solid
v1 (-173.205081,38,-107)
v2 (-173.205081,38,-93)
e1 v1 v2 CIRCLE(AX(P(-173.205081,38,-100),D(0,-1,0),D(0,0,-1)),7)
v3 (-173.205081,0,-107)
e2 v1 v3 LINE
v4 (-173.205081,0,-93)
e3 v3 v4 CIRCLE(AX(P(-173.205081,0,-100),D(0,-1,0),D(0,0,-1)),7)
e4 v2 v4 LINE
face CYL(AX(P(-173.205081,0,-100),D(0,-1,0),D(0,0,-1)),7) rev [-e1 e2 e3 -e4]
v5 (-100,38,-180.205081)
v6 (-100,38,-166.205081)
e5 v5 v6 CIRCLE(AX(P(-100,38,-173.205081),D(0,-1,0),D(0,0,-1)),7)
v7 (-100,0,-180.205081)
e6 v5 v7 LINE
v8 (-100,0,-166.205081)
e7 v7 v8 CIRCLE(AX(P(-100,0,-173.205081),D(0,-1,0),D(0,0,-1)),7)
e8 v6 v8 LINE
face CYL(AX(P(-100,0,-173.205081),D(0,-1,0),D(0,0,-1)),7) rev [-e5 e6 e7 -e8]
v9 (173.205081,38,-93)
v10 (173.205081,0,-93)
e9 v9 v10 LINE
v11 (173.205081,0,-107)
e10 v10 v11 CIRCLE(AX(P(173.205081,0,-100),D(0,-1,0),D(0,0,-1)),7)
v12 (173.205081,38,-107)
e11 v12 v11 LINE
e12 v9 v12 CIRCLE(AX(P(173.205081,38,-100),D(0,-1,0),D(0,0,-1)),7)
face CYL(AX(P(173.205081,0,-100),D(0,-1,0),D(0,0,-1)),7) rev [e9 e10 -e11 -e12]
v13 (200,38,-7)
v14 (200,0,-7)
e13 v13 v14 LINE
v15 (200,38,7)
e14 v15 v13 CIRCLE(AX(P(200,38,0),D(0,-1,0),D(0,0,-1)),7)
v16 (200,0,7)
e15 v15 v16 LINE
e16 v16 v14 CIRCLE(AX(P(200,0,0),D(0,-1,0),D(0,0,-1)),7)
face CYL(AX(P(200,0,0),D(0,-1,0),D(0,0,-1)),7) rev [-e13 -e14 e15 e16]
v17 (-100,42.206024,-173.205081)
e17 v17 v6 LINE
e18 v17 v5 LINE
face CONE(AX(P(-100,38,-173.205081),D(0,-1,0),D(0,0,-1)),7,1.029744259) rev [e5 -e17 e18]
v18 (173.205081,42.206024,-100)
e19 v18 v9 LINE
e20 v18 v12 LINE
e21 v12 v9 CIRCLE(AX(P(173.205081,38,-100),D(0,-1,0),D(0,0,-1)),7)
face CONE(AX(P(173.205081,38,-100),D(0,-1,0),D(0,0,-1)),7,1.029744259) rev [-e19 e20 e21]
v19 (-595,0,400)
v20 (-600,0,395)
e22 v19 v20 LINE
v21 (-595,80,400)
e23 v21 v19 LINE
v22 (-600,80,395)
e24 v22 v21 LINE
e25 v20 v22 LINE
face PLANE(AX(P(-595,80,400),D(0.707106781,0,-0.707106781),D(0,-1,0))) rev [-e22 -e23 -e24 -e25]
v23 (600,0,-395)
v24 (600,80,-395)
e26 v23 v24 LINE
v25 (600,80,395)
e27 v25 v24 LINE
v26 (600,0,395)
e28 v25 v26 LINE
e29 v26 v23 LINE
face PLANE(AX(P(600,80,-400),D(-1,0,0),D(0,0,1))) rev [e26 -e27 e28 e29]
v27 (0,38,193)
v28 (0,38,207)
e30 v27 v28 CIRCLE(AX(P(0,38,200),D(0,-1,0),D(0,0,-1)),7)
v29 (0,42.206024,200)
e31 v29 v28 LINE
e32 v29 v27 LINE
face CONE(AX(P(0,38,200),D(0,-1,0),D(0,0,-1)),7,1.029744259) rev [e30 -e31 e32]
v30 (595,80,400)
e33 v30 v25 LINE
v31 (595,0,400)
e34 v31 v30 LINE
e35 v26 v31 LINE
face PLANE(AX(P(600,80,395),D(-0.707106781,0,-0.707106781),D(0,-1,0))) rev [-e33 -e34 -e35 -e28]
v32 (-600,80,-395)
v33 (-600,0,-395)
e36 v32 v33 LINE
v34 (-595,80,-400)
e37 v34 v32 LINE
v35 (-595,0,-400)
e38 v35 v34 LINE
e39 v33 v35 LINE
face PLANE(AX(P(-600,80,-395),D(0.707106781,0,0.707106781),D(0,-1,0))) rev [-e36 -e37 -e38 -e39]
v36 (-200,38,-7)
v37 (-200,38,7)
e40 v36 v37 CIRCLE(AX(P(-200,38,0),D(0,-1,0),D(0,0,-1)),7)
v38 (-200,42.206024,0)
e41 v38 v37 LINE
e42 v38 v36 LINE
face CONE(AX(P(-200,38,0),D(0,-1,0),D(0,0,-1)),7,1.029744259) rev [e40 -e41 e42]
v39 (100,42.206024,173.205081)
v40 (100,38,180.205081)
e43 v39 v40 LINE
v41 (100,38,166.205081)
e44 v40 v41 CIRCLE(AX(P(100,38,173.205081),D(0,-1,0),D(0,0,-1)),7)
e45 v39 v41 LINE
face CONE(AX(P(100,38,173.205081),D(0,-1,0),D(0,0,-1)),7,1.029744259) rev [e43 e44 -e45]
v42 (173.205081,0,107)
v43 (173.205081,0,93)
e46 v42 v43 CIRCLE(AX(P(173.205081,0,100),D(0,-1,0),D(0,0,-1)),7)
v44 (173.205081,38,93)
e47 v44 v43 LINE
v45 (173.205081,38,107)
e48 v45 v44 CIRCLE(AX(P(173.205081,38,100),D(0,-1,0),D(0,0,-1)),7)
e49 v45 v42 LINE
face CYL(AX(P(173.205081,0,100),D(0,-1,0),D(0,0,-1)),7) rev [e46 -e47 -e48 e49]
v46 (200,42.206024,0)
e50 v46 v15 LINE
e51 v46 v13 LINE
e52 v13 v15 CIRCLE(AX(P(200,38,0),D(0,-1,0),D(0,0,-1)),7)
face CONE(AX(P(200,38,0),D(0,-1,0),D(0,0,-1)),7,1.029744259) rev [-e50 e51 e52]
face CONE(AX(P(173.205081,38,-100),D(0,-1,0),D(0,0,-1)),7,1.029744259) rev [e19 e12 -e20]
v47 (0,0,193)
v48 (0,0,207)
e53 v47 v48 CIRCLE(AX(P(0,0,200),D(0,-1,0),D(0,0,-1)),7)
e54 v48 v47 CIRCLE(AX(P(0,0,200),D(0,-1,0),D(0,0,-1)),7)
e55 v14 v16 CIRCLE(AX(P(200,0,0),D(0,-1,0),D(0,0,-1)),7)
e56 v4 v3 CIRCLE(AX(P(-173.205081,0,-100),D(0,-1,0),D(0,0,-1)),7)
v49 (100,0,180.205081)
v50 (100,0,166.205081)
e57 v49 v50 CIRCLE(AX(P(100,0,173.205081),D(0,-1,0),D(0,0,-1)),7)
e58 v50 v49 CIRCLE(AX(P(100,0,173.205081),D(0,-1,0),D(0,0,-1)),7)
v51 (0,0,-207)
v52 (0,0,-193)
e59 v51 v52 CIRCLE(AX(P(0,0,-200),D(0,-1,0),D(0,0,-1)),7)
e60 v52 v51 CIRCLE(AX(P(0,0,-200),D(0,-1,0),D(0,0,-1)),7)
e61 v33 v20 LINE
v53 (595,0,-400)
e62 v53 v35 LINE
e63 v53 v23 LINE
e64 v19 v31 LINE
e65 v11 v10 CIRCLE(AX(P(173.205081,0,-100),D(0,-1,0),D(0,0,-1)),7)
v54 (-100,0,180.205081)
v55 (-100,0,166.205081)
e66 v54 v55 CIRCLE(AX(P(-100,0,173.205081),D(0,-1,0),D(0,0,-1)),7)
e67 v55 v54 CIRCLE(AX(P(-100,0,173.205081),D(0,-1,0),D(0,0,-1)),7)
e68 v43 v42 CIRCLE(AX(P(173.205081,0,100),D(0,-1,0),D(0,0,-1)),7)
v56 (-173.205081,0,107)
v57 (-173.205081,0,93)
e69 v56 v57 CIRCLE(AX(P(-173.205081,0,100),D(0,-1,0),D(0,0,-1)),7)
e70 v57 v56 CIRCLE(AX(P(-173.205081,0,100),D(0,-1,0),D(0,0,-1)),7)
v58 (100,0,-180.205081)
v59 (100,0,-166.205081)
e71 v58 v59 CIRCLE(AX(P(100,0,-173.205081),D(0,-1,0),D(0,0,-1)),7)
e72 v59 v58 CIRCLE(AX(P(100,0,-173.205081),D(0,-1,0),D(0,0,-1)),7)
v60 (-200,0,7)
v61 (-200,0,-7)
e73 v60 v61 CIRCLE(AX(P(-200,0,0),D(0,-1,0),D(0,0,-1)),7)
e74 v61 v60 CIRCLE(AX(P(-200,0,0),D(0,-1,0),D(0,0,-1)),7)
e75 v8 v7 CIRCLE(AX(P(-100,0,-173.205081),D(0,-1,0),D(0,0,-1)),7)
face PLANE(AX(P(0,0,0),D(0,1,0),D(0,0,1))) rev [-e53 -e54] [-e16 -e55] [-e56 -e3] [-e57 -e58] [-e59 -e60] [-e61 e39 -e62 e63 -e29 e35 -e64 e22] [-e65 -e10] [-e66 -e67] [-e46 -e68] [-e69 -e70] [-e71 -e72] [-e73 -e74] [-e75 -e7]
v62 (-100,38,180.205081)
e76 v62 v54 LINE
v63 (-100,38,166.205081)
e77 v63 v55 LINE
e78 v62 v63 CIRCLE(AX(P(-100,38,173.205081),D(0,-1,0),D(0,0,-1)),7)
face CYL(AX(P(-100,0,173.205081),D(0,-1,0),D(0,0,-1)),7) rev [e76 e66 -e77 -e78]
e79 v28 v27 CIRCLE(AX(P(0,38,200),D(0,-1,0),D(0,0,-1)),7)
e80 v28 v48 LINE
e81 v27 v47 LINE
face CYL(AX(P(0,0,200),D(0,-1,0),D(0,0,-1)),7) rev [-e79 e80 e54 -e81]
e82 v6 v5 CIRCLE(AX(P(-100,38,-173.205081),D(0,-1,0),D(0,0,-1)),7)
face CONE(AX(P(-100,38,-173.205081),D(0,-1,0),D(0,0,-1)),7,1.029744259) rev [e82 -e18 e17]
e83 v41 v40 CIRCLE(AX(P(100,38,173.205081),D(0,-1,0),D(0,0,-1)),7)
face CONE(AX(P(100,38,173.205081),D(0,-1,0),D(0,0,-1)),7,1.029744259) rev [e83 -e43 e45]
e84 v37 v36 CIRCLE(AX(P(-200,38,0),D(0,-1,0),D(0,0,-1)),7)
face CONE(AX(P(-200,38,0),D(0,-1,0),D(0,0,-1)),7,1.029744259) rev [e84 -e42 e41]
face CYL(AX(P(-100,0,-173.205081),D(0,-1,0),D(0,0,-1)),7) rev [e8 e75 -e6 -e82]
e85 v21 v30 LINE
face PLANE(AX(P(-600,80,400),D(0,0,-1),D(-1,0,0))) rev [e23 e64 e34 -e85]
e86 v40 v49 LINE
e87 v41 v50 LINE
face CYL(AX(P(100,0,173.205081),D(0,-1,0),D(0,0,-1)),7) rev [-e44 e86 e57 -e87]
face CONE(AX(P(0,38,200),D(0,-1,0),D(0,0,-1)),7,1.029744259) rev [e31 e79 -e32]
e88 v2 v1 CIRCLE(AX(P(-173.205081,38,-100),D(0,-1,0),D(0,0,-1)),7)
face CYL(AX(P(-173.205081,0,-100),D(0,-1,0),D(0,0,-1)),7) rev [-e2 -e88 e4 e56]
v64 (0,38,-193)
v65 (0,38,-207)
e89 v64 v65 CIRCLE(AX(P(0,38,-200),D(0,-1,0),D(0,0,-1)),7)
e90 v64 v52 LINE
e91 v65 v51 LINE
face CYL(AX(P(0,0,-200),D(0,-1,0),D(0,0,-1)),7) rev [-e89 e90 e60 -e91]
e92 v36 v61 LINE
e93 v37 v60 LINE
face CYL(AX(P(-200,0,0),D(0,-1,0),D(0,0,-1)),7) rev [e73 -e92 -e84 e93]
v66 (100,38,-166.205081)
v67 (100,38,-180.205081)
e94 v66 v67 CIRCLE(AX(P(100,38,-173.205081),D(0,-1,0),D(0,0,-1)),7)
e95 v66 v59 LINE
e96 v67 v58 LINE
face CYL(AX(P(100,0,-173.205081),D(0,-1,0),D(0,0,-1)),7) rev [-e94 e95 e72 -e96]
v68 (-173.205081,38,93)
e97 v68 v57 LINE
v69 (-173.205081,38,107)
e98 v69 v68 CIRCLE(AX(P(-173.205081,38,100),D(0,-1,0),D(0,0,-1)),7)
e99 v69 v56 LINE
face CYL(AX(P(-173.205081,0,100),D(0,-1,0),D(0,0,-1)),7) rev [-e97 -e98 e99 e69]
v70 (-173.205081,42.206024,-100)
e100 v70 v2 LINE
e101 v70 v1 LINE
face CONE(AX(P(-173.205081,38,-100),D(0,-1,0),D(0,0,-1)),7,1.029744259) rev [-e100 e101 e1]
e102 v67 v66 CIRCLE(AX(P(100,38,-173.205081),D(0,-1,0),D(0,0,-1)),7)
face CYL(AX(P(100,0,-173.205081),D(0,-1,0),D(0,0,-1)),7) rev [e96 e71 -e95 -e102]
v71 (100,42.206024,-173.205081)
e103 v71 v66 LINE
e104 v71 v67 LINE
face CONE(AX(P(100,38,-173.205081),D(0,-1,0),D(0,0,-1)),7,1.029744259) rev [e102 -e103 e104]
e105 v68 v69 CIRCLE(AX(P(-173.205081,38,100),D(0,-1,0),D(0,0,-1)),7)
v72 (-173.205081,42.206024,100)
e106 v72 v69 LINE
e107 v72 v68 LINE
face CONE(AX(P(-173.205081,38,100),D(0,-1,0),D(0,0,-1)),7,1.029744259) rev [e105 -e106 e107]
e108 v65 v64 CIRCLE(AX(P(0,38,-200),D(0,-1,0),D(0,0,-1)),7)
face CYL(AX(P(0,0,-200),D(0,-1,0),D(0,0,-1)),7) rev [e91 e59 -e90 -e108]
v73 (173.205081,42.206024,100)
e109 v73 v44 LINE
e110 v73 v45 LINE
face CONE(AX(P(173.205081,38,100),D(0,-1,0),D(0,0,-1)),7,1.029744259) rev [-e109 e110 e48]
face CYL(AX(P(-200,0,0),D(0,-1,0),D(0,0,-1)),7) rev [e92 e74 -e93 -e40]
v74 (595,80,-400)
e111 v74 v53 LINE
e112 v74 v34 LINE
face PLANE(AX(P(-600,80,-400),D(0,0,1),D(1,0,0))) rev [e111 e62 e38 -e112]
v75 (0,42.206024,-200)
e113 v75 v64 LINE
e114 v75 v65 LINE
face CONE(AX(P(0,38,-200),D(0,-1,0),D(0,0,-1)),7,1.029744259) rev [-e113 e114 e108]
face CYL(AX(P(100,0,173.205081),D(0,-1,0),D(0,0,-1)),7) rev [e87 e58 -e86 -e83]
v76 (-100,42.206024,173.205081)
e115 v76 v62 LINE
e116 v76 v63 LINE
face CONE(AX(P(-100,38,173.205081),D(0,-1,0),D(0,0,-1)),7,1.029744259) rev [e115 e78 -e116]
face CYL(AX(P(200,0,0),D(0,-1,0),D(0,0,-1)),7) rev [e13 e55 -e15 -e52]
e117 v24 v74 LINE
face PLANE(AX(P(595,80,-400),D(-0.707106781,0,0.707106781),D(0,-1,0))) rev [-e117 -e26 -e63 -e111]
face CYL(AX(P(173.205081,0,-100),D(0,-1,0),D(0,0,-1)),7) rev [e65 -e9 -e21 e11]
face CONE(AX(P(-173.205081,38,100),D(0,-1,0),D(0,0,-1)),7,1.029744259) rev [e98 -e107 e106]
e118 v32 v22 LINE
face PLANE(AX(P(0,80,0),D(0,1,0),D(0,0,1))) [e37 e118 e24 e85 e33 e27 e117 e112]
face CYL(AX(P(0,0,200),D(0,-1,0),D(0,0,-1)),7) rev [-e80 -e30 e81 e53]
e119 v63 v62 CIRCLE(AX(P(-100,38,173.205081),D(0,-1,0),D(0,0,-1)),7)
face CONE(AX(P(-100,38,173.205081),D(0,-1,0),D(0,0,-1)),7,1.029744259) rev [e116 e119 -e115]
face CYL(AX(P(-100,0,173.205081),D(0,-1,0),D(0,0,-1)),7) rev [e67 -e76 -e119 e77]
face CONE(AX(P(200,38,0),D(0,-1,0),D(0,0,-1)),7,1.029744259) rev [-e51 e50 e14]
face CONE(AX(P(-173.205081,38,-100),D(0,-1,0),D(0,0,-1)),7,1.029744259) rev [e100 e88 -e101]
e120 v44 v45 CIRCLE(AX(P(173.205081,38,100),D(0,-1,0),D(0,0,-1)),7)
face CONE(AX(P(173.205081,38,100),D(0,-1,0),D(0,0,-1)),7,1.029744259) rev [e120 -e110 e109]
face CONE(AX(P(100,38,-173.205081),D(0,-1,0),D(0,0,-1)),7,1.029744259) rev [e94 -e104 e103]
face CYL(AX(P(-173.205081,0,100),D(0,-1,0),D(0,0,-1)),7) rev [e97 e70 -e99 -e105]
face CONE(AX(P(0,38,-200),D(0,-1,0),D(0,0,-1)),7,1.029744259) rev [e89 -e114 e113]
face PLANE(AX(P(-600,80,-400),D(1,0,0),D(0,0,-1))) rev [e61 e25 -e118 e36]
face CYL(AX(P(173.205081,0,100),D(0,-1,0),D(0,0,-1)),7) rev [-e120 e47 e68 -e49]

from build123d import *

# Parameters (mm, degrees)
SKETCH1_W              = 1200
SKETCH1_H              = 800
BOSS_EXTRUDE1_DEPTH    = 80
CHAMFER1_SIZE          = 5
M16_TAPPED_HOLE1_D     = 14
M16_TAPPED_HOLE1_DEPTH = 38
M16_TAPPED_HOLE1_TIP   = 4.206024333


with BuildPart() as part:
    # Sketch1 → Boss-Extrude1 (new body)
    with BuildSketch(Plane(origin=(0, 0, 0), x_dir=(1, 0, 0), z_dir=(0, 1, 0))):
        Rectangle(SKETCH1_W, SKETCH1_H)
    extrude(amount=BOSS_EXTRUDE1_DEPTH)

    # Chamfer1
    chamfer1_edges = [part.edges().sort_by_distance(p)[0] for p in [
        (600, 40, 400),
        (-600, 40, 400),
        (-600, 40, -400),
        (600, 40, -400),
    ]]
    chamfer(chamfer1_edges, length=CHAMFER1_SIZE)

    # M16 Tapped Hole1
    with Locations(Plane(origin=(0, 0, 0), x_dir=(-1, 0, 0), z_dir=(0, -1, 0))):
        with Locations((0, -200), (100, -173.205080757), (173.205080757, -100), (200, 0), (173.205080757, 100), (100, 173.205080757), (0, 200), (-100, 173.205080757), (-173.205080757, 100), (-200, 0), (-173.205080757, -100), (-100, -173.205080757)):
            Hole(M16_TAPPED_HOLE1_D / 2, depth=M16_TAPPED_HOLE1_DEPTH)
            with Locations((0, 0, -(M16_TAPPED_HOLE1_DEPTH + M16_TAPPED_HOLE1_TIP / 2))):  # 118° drill point
                Cone(0, M16_TAPPED_HOLE1_D / 2, M16_TAPPED_HOLE1_TIP, mode=Mode.SUBTRACT)


solid = part.part
